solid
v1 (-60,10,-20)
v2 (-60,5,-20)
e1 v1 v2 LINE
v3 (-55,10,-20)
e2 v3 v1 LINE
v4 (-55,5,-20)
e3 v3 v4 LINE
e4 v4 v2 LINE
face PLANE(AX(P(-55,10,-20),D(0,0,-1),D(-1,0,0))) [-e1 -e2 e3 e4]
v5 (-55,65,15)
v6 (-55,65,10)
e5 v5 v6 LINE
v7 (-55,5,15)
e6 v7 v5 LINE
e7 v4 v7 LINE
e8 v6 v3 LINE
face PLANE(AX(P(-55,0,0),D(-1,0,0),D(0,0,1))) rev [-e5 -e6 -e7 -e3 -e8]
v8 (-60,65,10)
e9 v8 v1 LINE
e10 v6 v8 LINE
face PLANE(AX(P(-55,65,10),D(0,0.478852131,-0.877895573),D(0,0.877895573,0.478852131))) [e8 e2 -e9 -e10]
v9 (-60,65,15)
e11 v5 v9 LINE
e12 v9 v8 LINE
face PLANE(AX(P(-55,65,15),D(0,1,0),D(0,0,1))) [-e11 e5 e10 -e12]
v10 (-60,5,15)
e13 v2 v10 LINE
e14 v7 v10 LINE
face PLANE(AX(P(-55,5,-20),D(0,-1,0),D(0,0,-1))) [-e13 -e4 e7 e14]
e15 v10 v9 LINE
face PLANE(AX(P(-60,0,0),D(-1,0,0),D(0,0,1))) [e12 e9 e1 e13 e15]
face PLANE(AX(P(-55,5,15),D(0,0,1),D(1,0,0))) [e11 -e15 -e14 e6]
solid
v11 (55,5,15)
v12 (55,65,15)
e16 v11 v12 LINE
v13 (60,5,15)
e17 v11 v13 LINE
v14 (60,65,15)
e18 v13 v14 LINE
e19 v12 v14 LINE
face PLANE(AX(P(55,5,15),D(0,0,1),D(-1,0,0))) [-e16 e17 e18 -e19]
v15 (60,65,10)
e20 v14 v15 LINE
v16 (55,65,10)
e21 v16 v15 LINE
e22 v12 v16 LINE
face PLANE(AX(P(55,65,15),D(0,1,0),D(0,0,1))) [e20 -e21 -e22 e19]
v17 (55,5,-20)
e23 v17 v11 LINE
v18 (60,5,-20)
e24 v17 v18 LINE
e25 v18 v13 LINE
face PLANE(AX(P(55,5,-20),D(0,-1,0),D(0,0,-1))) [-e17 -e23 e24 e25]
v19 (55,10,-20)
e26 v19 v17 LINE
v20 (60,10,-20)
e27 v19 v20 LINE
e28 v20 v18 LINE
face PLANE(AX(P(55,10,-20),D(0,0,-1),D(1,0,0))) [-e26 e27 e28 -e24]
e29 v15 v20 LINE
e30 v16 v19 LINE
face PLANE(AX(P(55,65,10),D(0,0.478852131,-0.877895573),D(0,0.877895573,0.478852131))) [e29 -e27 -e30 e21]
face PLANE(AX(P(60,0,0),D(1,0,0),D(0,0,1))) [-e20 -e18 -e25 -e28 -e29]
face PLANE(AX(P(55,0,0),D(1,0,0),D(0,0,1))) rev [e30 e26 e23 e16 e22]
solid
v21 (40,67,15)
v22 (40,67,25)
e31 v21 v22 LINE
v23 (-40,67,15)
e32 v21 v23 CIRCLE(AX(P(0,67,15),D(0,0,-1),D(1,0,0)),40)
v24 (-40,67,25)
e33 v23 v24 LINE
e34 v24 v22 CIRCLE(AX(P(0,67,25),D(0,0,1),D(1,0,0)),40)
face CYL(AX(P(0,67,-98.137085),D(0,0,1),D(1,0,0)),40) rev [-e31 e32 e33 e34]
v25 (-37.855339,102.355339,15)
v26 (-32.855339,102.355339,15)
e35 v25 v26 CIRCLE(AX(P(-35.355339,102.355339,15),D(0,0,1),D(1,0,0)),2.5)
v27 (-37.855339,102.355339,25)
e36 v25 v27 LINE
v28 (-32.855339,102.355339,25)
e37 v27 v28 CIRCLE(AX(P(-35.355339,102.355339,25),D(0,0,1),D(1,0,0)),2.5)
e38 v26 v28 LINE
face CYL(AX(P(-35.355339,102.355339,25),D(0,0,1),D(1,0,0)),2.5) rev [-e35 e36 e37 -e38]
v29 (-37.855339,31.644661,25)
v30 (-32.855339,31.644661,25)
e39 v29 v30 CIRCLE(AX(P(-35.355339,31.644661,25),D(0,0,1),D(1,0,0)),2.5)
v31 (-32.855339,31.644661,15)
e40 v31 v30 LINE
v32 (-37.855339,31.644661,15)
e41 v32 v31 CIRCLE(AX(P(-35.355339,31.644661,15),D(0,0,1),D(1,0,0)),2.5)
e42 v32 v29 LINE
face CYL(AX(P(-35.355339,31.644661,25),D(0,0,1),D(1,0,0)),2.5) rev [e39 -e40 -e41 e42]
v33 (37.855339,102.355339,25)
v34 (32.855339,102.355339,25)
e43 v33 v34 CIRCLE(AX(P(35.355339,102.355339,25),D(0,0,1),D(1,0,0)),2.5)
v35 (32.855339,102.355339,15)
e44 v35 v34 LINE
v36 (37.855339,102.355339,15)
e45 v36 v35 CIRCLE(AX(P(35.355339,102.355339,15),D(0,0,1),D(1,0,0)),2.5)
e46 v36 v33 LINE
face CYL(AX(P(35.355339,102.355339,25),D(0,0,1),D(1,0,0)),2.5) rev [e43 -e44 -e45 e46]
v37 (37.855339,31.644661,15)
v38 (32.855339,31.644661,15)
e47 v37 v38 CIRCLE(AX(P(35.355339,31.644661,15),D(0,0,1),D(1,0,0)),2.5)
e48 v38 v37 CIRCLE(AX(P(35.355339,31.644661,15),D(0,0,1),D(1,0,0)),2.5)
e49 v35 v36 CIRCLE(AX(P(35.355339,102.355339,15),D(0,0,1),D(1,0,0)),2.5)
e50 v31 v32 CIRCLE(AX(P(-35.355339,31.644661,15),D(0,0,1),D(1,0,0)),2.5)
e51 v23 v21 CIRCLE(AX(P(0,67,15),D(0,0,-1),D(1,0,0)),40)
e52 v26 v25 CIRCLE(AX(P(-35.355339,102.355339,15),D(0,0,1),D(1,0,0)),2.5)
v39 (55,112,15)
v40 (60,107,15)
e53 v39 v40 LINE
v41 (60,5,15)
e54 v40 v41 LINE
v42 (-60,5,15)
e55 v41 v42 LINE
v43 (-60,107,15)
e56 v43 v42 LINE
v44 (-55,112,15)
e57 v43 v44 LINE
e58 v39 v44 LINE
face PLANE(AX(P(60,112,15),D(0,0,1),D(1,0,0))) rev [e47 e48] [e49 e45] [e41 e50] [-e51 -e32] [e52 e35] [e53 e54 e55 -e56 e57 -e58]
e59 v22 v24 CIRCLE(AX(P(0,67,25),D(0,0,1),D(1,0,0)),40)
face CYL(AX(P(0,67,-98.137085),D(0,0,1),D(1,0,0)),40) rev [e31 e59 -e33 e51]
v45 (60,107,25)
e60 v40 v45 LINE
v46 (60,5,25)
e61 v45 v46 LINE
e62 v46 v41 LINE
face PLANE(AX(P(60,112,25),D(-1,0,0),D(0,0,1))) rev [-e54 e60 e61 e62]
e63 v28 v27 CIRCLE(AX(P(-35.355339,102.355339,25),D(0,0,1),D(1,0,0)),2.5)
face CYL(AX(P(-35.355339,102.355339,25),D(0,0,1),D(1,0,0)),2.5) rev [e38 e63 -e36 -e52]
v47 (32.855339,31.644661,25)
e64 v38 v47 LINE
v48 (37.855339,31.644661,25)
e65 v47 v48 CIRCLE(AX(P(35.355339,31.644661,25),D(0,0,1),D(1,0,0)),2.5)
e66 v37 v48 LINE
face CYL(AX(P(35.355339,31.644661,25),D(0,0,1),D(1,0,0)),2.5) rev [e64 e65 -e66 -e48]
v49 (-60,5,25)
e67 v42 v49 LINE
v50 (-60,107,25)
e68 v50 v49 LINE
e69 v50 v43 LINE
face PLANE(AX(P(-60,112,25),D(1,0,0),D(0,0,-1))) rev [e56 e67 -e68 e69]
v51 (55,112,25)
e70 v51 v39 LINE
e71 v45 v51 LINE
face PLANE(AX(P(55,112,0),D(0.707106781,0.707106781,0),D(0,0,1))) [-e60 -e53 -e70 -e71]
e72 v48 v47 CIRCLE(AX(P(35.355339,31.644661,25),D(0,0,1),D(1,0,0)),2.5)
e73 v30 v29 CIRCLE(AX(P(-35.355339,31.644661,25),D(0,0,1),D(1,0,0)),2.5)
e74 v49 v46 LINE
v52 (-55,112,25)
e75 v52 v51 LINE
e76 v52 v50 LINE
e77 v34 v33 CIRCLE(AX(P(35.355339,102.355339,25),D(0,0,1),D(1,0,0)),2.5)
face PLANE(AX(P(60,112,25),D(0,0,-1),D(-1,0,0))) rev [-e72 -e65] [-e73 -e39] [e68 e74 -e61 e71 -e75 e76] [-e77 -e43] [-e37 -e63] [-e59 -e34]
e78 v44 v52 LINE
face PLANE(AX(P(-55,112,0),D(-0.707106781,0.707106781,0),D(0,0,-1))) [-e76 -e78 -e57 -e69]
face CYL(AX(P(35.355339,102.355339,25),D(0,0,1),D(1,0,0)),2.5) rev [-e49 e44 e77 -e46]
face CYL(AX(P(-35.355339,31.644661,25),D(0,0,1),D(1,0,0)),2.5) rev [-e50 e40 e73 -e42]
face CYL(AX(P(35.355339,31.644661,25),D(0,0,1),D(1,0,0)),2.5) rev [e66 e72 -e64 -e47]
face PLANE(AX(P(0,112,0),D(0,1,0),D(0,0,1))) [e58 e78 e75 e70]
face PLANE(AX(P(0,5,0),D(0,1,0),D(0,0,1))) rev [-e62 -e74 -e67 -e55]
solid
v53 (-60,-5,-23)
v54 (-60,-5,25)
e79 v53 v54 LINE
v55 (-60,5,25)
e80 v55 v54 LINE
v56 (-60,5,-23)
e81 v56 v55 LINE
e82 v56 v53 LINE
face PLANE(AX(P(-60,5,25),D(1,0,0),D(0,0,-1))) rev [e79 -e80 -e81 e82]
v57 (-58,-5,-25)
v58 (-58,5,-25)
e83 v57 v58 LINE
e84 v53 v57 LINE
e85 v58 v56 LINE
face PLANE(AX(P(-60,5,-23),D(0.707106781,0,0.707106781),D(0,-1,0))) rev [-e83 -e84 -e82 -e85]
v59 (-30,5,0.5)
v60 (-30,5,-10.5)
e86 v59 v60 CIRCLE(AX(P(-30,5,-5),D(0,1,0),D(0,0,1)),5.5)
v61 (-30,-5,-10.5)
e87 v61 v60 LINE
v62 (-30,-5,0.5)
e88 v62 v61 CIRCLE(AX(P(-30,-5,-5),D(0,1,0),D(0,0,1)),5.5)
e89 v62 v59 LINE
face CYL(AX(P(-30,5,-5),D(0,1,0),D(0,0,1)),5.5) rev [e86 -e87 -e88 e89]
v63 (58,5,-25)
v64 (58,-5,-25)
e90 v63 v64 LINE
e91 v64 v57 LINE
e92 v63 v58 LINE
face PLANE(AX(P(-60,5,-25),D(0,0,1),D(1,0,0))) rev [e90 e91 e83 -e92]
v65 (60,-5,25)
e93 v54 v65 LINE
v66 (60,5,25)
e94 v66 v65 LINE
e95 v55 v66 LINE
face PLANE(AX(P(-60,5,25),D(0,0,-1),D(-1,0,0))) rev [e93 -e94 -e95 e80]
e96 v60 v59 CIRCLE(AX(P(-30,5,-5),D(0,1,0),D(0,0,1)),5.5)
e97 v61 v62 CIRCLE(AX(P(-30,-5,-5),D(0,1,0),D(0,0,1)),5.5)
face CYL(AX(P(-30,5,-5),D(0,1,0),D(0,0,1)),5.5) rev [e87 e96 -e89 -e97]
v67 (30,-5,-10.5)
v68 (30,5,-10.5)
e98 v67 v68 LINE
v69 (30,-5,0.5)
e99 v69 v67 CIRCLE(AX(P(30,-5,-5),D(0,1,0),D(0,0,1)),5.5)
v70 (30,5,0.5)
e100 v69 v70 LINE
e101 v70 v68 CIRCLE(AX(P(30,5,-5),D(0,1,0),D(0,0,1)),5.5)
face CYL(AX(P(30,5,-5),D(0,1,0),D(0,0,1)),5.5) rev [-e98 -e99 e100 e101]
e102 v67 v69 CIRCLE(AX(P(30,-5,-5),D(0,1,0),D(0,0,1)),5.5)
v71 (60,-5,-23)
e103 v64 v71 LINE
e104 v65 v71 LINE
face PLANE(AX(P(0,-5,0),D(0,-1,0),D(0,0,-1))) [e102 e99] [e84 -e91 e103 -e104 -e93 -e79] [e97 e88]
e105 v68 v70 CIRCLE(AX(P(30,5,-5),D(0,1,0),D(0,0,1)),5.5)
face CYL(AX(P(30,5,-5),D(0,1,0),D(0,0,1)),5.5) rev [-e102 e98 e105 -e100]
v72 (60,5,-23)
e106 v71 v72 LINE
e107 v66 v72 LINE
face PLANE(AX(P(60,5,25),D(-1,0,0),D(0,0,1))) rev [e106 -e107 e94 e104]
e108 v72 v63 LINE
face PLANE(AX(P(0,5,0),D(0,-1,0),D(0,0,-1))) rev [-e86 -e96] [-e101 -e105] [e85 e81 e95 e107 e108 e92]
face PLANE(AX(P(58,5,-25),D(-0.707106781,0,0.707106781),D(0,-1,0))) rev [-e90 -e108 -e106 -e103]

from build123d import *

# Parameters (mm, degrees)
SKETCH_1_W                   = 120
SKETCH_1_H                   = 50
EXTRUDE_1_DEPTH              = 5
SKETCH_2_W                   = 120
SKETCH_2_H                   = 10
EXTRUDE_2_DEPTH              = 107
CHAMFER_1_SIZE               = 5
CHAMFER_2_SIZE               = 2
EXTRUDE_3_DEPTH              = 5
SKETCH_4_R                   = 40
CUT_EXTRUDE_1_DEPTH          = 10
SKETCH_6_W                   = 5.5
SKETCH_6_H                   = 10
HOLE_WIZARD_M10_1_AT_2_COUNT = 2
HOLE_WIZARD_M10_1_AT_2_PITCH = 60
HOLE_WIZARD_M6_1_AT_2_COUNT  = 2
HOLE_WIZARD_M6_1_AT_2_PITCH  = 70.710678119
HOLE_WIZARD_M6_1_AT_3_COUNT  = 2
HOLE_WIZARD_M6_1_AT_3_PITCH  = 100
HOLE_WIZARD_M6_1_AT_4_COUNT  = 2
HOLE_WIZARD_M6_1_AT_4_PITCH  = 70.710678119


with BuildPart() as part:
    # 草图1 → 凸台-拉伸1 (new, symmetric)
    with BuildSketch(Plane(origin=(0, 0, 0), x_dir=(1, 0, 0), z_dir=(0, 1, 0))):
        Rectangle(SKETCH_1_W, SKETCH_1_H)
    extrude(amount=EXTRUDE_1_DEPTH, both=True)

    # 倒角2
    chamfer_2_edges = [part.edges().sort_by_distance(p)[0] for p in [
        (-60, 0, -25),
        (60, 0, -25),
    ]]
    chamfer(chamfer_2_edges, length=CHAMFER_2_SIZE)

    # 草图6 → M10 间隙孔1 (revolve, cut)
    with BuildSketch(Plane(origin=(30, 5, -5), x_dir=(0, 0, 1), z_dir=(1, 0, 0))):
        with Locations((2.75, 5)):
            Rectangle(SKETCH_6_W, SKETCH_6_H)
    hole_wizard_m10_1 = revolve(axis=Axis((30, 11.35, -5), (0, -1, 0)), mode=Mode.SUBTRACT)

    # M10 间隙孔1 at 2: M10 间隙孔1 ×2
    with Locations(*[(-i * HOLE_WIZARD_M10_1_AT_2_PITCH, 0, 0) for i in range(1, HOLE_WIZARD_M10_1_AT_2_COUNT)]):
        add(hole_wizard_m10_1, mode=Mode.SUBTRACT)


with BuildPart() as body_2:
    # 草图2 → 凸台-拉伸2 (new body)
    with BuildSketch(Plane(origin=(0, 5, 0), x_dir=(1, 0, 0), z_dir=(0, 1, 0))):
        with Locations((0, -20)):
            Rectangle(SKETCH_2_W, SKETCH_2_H)
    extrude(amount=EXTRUDE_2_DEPTH)

    # 倒角1
    chamfer_1_edges = [body_2.edges().sort_by_distance(p)[0] for p in [
        (-60, 112, 20),
        (60, 112, 20),
    ]]
    chamfer(chamfer_1_edges, length=CHAMFER_1_SIZE)

    # 草图4 → 切除-拉伸1 (cut)
    with BuildSketch(Plane.XY.offset(25)):
        with Locations((0, 67)):
            Circle(SKETCH_4_R)
    extrude(amount=-CUT_EXTRUDE_1_DEPTH, mode=Mode.SUBTRACT)

    # 草图8 → M6 螺纹孔1 (revolve, cut)
    with BuildSketch(Plane(origin=(-35.355339059, 102.355339059, 25), x_dir=(0, -1, 0), z_dir=(1, 0, 0))):
        Polygon((0, 0), (0, 16.502151548), (2.5, 15), (2.5, 0), align=None)
    hole_wizard_m6_1 = revolve(axis=Axis((-35.355339059, 102.355339059, 31.35), (0, 0, -1)), mode=Mode.SUBTRACT)

    # M6 螺纹孔1 at 2: M6 螺纹孔1 ×2
    with Locations(*[(i * HOLE_WIZARD_M6_1_AT_2_PITCH, 0, 0) for i in range(1, HOLE_WIZARD_M6_1_AT_2_COUNT)]):
        add(hole_wizard_m6_1, mode=Mode.SUBTRACT)

    # M6 螺纹孔1 at 3: M6 螺纹孔1 ×2
    with Locations(*[Vector(0.7071067811865476, -0.7071067811865476, 0) * (i * HOLE_WIZARD_M6_1_AT_3_PITCH) for i in range(1, HOLE_WIZARD_M6_1_AT_3_COUNT)]):
        add(hole_wizard_m6_1, mode=Mode.SUBTRACT)

    # M6 螺纹孔1 at 4: M6 螺纹孔1 ×2
    with Locations(*[(0, -i * HOLE_WIZARD_M6_1_AT_4_PITCH, 0) for i in range(1, HOLE_WIZARD_M6_1_AT_4_COUNT)]):
        add(hole_wizard_m6_1, mode=Mode.SUBTRACT)


with BuildPart() as body_3:
    # 草图3 → 凸台-拉伸3 (new body)
    with BuildSketch(Plane.ZY.offset(60)):
        Polygon((15, 65), (10, 65), (-20, 10), (-20, 5), (15, 5), align=None)
    extrude(amount=-EXTRUDE_3_DEPTH)


with BuildPart() as body_4:
    # 镜向1: mirrored copy
    add(body_3.part.mirror(Plane(origin=(0, 0, 0), x_dir=(0, 0, 1), z_dir=(1, 0, 0))))


solid = Compound([part.part, body_2.part, body_3.part, body_4.part])
